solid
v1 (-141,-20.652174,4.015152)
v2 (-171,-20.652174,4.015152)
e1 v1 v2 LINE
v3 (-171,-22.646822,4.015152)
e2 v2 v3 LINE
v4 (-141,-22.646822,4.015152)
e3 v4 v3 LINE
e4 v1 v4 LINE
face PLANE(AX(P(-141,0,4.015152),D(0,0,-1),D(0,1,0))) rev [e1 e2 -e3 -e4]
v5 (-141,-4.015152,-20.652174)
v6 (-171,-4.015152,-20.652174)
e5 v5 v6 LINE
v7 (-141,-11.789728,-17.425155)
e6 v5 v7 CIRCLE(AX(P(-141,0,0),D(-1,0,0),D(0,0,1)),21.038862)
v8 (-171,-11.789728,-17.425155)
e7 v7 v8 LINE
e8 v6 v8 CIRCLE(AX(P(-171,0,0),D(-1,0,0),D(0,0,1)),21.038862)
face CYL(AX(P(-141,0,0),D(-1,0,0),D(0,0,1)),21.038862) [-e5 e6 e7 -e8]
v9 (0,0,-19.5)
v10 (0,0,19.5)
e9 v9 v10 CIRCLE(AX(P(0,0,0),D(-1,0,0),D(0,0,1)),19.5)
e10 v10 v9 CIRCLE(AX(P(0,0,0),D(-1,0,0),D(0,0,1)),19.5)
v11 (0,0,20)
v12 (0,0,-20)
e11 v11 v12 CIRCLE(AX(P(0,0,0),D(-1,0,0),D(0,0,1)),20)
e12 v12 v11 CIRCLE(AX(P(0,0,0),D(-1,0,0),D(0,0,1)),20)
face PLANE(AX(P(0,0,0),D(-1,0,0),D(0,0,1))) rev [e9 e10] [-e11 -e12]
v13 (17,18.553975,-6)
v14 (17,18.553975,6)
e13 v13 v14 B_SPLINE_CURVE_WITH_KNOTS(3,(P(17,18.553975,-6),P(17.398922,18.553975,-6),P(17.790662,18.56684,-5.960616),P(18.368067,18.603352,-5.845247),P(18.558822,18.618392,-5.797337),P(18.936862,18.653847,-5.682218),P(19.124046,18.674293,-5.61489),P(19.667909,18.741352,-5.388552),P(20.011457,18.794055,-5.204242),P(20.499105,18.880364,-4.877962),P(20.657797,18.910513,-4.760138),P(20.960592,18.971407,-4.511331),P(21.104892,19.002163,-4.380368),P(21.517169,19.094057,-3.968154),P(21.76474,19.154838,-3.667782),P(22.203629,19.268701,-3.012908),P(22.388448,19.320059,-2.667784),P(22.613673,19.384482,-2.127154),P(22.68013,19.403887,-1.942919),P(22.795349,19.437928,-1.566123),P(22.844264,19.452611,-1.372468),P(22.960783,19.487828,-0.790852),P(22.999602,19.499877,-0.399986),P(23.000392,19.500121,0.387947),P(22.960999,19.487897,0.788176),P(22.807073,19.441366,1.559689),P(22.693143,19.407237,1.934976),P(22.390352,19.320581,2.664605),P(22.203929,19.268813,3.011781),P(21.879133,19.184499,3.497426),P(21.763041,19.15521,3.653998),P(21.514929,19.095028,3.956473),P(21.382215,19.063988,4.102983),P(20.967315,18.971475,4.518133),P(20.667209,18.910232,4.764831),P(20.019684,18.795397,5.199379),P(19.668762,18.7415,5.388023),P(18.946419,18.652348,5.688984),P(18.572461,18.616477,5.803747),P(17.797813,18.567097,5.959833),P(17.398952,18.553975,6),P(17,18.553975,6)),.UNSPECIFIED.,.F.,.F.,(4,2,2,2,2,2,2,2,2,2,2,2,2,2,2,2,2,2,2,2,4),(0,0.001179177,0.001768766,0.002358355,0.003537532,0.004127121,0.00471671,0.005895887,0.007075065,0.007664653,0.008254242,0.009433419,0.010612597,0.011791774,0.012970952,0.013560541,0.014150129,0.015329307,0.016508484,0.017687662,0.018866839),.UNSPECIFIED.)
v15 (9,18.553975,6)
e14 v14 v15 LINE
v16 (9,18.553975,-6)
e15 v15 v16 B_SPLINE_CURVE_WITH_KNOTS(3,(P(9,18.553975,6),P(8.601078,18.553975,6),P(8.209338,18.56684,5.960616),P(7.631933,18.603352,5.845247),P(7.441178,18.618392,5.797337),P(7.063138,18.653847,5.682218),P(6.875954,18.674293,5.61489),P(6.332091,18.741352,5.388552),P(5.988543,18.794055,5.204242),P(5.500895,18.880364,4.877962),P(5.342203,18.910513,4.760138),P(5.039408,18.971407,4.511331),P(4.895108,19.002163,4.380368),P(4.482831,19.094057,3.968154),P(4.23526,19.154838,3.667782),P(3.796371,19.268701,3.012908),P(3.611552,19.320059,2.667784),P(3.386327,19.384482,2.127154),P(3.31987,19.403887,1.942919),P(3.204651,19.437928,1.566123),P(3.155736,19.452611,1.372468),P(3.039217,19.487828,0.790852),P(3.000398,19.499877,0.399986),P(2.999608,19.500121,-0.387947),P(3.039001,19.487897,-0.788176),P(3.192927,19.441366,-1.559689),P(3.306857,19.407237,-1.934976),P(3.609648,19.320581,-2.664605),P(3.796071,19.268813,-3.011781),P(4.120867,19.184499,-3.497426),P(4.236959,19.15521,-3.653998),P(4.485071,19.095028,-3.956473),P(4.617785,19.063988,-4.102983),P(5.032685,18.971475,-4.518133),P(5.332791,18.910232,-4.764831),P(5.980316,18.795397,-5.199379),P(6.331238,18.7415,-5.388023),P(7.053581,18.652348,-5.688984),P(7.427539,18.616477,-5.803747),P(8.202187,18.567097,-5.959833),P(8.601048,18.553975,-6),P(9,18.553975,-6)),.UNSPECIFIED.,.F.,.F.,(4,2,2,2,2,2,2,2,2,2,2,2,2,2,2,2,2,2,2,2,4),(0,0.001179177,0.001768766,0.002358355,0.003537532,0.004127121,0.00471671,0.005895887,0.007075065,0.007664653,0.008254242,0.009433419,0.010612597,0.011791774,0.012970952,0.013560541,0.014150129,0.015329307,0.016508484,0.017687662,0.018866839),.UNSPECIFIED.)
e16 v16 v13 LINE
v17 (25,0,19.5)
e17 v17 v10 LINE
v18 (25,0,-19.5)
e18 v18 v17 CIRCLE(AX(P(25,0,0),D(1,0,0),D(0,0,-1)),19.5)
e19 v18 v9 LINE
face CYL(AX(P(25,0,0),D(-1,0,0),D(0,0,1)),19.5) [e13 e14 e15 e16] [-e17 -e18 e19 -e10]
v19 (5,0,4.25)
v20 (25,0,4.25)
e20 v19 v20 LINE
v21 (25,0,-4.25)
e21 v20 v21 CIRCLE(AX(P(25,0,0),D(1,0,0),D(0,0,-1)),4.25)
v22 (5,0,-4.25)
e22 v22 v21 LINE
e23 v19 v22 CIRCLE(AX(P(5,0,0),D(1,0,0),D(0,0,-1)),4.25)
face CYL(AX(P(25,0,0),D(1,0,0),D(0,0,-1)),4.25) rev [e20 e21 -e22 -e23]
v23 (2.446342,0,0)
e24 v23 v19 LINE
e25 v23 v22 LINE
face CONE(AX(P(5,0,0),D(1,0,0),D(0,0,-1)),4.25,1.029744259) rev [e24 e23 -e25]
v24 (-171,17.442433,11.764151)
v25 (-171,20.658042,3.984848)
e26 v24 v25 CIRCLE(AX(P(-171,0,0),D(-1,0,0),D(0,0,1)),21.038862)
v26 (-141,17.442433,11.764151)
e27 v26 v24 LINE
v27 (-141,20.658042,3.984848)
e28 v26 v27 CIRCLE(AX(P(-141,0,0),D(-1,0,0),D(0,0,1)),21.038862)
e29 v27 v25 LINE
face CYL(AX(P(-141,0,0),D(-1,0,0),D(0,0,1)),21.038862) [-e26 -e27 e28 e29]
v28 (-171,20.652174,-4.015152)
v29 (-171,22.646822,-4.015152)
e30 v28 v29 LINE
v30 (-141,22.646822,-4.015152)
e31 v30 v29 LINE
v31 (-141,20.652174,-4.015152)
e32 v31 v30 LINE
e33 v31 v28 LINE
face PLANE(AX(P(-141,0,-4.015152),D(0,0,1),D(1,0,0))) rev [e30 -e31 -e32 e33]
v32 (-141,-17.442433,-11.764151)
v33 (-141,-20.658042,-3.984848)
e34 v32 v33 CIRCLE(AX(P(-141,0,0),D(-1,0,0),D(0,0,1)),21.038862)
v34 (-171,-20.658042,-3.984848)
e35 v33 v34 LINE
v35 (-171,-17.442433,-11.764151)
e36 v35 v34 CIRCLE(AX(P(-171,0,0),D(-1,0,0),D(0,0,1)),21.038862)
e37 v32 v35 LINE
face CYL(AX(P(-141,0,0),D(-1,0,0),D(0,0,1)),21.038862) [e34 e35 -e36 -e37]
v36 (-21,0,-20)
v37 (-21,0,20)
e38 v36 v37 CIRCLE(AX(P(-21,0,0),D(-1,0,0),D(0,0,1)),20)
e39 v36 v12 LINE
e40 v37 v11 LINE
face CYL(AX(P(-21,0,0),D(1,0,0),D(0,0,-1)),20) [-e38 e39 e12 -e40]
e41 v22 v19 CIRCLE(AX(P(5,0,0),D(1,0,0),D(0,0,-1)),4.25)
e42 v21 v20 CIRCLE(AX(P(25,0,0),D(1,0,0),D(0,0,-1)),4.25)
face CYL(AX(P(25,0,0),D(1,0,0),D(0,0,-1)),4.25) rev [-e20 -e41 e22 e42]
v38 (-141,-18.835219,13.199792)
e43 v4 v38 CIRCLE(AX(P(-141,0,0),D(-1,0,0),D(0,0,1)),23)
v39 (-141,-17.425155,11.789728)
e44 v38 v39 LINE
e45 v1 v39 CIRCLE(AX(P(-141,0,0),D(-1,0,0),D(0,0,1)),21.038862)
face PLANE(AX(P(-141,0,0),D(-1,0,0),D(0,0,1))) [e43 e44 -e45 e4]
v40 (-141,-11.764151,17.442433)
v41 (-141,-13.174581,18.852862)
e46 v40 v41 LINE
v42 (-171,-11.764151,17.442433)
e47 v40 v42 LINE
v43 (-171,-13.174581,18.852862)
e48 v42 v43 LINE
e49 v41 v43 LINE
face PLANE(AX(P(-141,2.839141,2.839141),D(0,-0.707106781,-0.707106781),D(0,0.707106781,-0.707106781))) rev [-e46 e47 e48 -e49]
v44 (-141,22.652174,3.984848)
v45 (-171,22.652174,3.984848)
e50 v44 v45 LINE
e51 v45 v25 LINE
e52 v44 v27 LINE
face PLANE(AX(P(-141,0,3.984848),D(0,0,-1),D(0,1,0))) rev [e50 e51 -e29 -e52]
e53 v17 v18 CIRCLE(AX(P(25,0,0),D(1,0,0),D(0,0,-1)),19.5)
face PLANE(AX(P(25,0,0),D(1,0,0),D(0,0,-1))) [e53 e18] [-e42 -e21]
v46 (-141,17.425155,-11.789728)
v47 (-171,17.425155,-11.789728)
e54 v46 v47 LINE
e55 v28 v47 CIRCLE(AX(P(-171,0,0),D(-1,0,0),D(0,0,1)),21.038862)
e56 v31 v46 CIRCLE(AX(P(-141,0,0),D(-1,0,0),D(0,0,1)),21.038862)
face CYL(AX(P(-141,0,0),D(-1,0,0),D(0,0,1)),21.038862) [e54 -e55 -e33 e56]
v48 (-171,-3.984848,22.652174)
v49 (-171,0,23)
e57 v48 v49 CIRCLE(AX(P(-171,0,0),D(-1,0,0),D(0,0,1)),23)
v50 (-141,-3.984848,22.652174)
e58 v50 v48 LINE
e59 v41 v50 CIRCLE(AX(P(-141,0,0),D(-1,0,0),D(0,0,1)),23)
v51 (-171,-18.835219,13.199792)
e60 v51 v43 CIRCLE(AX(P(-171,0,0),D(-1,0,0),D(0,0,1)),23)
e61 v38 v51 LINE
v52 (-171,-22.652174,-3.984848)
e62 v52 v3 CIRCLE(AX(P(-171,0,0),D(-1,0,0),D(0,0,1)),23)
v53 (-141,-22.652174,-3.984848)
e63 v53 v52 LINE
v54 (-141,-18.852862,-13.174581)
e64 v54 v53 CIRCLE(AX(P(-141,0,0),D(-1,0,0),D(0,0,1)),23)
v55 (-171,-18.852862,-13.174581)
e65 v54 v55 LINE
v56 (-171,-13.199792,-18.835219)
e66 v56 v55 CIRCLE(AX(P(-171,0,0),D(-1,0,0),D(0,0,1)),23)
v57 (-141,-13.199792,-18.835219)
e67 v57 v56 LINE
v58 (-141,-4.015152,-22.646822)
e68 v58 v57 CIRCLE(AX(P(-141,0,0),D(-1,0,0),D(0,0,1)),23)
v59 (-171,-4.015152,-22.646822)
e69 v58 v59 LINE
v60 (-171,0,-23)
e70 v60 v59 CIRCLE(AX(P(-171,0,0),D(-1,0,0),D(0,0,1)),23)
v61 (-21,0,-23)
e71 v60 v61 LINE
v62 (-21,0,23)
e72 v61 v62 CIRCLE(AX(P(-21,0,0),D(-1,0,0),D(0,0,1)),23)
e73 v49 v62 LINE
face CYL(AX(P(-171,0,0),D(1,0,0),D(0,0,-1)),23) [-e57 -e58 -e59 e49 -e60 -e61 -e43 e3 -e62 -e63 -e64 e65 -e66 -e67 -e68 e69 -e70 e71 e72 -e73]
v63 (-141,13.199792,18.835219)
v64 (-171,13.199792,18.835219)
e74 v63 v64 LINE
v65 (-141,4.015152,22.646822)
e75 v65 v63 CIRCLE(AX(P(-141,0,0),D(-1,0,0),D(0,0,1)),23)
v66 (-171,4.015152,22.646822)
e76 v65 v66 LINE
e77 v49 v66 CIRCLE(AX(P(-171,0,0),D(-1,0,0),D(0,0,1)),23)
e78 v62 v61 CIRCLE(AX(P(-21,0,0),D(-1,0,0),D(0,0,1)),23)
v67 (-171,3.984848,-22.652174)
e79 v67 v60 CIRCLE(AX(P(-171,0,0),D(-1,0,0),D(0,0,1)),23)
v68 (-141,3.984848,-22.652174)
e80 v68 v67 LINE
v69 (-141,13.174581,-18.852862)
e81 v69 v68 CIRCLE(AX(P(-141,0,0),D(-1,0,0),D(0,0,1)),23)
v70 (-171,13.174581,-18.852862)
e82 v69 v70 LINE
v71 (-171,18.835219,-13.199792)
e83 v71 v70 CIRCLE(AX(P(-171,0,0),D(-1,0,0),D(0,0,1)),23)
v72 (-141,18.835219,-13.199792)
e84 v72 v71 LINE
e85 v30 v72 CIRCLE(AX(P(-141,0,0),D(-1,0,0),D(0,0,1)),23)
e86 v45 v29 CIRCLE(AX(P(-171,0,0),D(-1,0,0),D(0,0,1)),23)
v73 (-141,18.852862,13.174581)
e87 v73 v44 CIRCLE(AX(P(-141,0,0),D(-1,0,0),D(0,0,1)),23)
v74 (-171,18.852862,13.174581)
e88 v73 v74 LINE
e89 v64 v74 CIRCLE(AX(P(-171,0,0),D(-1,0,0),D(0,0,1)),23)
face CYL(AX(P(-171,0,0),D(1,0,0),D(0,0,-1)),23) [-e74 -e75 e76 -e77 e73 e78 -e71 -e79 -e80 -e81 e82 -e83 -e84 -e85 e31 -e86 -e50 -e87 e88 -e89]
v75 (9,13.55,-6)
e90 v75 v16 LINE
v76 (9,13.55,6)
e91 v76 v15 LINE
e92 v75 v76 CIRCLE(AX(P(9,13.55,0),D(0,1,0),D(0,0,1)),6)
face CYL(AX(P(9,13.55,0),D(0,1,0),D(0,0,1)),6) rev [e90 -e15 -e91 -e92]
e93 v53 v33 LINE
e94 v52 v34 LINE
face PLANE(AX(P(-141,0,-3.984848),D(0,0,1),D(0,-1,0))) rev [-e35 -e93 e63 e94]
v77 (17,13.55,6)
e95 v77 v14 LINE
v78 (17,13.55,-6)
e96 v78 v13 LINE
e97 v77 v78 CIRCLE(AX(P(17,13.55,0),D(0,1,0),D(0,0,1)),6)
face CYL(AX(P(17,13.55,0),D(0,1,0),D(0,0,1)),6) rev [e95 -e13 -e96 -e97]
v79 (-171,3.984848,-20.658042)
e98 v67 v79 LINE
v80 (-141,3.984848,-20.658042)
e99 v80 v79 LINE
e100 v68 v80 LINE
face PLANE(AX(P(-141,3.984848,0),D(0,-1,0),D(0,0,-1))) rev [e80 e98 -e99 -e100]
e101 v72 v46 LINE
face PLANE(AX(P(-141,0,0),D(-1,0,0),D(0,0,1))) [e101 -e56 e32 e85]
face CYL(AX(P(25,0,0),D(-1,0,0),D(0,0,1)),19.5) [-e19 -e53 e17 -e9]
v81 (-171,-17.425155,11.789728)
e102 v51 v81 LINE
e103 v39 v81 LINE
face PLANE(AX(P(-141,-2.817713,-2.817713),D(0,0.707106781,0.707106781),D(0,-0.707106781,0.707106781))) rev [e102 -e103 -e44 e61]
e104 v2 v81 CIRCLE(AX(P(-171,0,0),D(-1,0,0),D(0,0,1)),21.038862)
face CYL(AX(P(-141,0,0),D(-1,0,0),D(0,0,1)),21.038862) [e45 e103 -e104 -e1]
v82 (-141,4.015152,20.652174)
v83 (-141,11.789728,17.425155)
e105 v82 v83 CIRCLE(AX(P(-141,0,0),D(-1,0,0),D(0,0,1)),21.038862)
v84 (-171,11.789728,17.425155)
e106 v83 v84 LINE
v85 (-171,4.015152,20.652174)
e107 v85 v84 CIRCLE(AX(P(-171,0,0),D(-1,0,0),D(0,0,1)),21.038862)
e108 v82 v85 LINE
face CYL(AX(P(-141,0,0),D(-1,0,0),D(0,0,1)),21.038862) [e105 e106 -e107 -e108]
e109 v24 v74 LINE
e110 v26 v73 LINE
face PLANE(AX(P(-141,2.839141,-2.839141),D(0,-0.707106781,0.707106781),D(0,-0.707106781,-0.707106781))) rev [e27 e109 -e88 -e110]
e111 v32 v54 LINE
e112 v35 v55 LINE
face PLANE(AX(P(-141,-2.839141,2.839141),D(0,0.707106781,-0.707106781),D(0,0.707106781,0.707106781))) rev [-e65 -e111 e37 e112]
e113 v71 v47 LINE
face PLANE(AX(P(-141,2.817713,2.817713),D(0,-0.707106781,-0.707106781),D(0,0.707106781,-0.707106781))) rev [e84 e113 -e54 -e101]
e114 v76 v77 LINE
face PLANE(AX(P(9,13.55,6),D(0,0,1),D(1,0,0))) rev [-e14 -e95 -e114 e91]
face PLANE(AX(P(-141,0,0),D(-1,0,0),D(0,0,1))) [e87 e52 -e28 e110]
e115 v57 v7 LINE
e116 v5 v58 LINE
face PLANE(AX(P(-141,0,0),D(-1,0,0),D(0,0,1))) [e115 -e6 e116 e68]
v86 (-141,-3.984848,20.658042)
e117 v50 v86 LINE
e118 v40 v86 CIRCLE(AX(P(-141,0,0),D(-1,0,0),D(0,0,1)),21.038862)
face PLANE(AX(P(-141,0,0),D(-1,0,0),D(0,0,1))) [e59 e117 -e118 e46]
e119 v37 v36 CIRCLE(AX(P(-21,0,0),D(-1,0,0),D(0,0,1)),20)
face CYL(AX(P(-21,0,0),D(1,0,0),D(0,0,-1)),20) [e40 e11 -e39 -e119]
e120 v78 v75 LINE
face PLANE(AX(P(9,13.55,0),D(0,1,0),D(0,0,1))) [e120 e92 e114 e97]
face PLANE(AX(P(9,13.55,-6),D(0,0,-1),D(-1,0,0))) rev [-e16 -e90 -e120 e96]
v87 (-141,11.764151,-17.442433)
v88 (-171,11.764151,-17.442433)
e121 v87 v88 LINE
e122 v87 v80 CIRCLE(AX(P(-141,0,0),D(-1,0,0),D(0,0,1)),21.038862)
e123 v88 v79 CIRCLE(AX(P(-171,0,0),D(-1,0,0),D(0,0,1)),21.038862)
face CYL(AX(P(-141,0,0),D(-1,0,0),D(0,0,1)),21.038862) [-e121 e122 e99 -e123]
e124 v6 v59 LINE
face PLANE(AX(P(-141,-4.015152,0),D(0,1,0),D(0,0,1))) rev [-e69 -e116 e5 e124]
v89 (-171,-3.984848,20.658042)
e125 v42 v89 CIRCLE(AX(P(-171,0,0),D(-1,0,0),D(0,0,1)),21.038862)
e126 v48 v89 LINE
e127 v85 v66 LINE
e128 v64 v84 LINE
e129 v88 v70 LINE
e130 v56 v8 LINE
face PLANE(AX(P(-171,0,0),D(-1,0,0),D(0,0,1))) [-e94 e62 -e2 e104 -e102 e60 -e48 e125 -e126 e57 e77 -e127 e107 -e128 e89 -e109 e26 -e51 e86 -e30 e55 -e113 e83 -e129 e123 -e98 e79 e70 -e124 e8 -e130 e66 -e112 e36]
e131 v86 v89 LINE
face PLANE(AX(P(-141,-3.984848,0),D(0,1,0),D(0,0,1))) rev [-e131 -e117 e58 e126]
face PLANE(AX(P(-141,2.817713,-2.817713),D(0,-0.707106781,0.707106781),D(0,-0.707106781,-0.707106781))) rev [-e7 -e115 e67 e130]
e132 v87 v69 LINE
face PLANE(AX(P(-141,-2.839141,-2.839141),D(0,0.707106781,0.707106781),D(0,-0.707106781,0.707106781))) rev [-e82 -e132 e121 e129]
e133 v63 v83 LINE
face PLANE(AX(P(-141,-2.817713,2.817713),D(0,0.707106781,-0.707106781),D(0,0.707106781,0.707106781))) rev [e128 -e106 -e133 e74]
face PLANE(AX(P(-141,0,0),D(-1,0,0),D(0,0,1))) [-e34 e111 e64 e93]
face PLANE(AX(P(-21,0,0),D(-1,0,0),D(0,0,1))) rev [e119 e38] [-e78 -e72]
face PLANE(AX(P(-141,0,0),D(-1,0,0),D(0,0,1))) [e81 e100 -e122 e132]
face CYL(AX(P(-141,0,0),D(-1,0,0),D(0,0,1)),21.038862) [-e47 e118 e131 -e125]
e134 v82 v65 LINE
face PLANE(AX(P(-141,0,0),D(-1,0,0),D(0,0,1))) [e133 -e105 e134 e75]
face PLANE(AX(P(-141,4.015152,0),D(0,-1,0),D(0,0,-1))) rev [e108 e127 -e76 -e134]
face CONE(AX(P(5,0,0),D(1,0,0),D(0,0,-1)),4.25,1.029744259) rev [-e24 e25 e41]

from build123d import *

# Parameters (mm, degrees)
SKETCH_1_R              = 19.5
EXTRUDE_1_DEPTH         = 25
CUT_EXTRUDE_1_DEPTH     = 5.95
SKETCH_3_R              = 20
EXTRUDE_2_DEPTH         = 21
SKETCH_4_R              = 23
EXTRUDE_3_DEPTH         = 150
CUT_EXTRUDE_START       = -30
CUT_EXTRUDE_2_DEPTH     = 30
HOLE_WIZARD_M10_1_D     = 8.5
HOLE_WIZARD_M10_1_DEPTH = 20
HOLE_WIZARD_M10_1_TIP   = 2.553657631


with BuildPart() as part:
    # 草图1 → 凸台-拉伸1 (new body)
    with BuildSketch(Plane(origin=(0, 0, 0), x_dir=(0, 0, -1), z_dir=(1, 0, 0))):
        Circle(SKETCH_1_R)
    extrude(amount=EXTRUDE_1_DEPTH)

    # 草图2 → 切除-拉伸1 (cut)
    with BuildSketch(Plane(origin=(0, 19.5, 0), x_dir=(1, 0, 0), z_dir=(0, 1, 0))):
        with BuildLine():
            Line((9, 6), (17, 6))
            ThreePointArc((17, 6), (23, 0), (17, -6))
            Line((17, -6), (9, -6))
            ThreePointArc((9, -6), (3, 0), (9, 6))
        make_face()
    extrude(amount=-CUT_EXTRUDE_1_DEPTH, mode=Mode.SUBTRACT)

    # 草图3 → 凸台-拉伸2 (add)
    with BuildSketch(Plane.ZY):
        with Locations(Location((0, 0, 0), (0, 0, 180))):
            Circle(SKETCH_3_R)
    extrude(amount=EXTRUDE_2_DEPTH)

    # 草图4 → 凸台-拉伸3 (add)
    with BuildSketch(Plane.ZY.offset(21)):
        Circle(SKETCH_4_R)
    extrude(amount=EXTRUDE_3_DEPTH)

    # 草图5 → 切除-拉伸2 (cut)
    with BuildSketch(Plane.ZY.offset(171).offset(CUT_EXTRUDE_START)):
        with BuildLine():
            ThreePointArc((18.852862485, -13.174580681), (21.255112475, -8.78750213), (22.652173913, -3.98484843))
            Line((22.652173913, -3.98484843), (20.658042319, -3.98484843))
            ThreePointArc((20.658042319, -3.98484843), (19.443275073, -8.036963599), (17.442433123, -11.764151318))
            Line((17.442433123, -11.764151318), (18.852862485, -13.174580681))
        make_face()
        with BuildLine():
            ThreePointArc((22.646822247, 4.01515157), (21.243336512, 8.81593182), (18.83521913, 13.199792435))
            Line((18.83521913, 13.199792435), (17.425155157, 11.789728463))
            ThreePointArc((17.425155157, 11.789728463), (19.431463114, 8.065480192), (20.652173913, 4.01515157))
            Line((20.652173913, 4.01515157), (22.646822247, 4.01515157))
        make_face()
        with BuildLine():
            Line((-20.652173913, -4.01515157), (-22.646822247, -4.01515157))
            ThreePointArc((-22.646822247, -4.01515157), (-21.243336512, -8.81593182), (-18.83521913, -13.199792435))
            Line((-18.83521913, -13.199792435), (-17.425155157, -11.789728463))
            ThreePointArc((-17.425155157, -11.789728463), (-19.431463114, -8.065480192), (-20.652173913, -4.01515157))
        make_face()
        with BuildLine():
            Line((-11.764151318, -17.442433123), (-13.174580681, -18.852862485))
            ThreePointArc((-13.174580681, -18.852862485), (-8.78750213, -21.255112475), (-3.98484843, -22.652173913))
            Line((-3.98484843, -22.652173913), (-3.98484843, -20.658042319))
            ThreePointArc((-3.98484843, -20.658042319), (-8.036963599, -19.443275073), (-11.764151318, -17.442433123))
        make_face()
        with BuildLine():
            ThreePointArc((4.01515157, -22.646822247), (8.81593182, -21.243336512), (13.199792435, -18.83521913))
            Line((13.199792435, -18.83521913), (11.789728463, -17.425155157))
            ThreePointArc((11.789728463, -17.425155157), (8.065480192, -19.431463114), (4.01515157, -20.652173913))
            Line((4.01515157, -20.652173913), (4.01515157, -22.646822247))
        make_face()
        with BuildLine():
            ThreePointArc((13.174580681, 18.852862485), (8.78750213, 21.255112475), (3.98484843, 22.652173913))
            Line((3.98484843, 22.652173913), (3.98484843, 20.658042319))
            ThreePointArc((3.98484843, 20.658042319), (8.036963599, 19.443275073), (11.764151318, 17.442433123))
            Line((11.764151318, 17.442433123), (13.174580681, 18.852862485))
        make_face()
        with BuildLine():
            Line((-4.01515157, 20.652173913), (-4.01515157, 22.646822247))
            ThreePointArc((-4.01515157, 22.646822247), (-8.81593182, 21.243336512), (-13.199792435, 18.83521913))
            Line((-13.199792435, 18.83521913), (-11.789728463, 17.425155157))
            ThreePointArc((-11.789728463, 17.425155157), (-8.065480192, 19.431463114), (-4.01515157, 20.652173913))
        make_face()
        with BuildLine():
            Line((-17.442433123, 11.764151318), (-18.852862485, 13.174580681))
            ThreePointArc((-18.852862485, 13.174580681), (-21.255112475, 8.78750213), (-22.652173913, 3.98484843))
            Line((-22.652173913, 3.98484843), (-20.658042319, 3.98484843))
            ThreePointArc((-20.658042319, 3.98484843), (-19.443275073, 8.036963599), (-17.442433123, 11.764151318))
        make_face()
    extrude(amount=CUT_EXTRUDE_2_DEPTH, mode=Mode.SUBTRACT)

    # M10 螺纹孔1
    with Locations(Plane(origin=(25, 0, 0), x_dir=(0, 0, -1), z_dir=(1, 0, 0))):
        with Locations((0, 0)):
            Hole(HOLE_WIZARD_M10_1_D / 2, depth=HOLE_WIZARD_M10_1_DEPTH)
            with Locations((0, 0, -(HOLE_WIZARD_M10_1_DEPTH + HOLE_WIZARD_M10_1_TIP / 2))):  # 118° drill point
                Cone(0, HOLE_WIZARD_M10_1_D / 2, HOLE_WIZARD_M10_1_TIP, mode=Mode.SUBTRACT)


solid = part.part
